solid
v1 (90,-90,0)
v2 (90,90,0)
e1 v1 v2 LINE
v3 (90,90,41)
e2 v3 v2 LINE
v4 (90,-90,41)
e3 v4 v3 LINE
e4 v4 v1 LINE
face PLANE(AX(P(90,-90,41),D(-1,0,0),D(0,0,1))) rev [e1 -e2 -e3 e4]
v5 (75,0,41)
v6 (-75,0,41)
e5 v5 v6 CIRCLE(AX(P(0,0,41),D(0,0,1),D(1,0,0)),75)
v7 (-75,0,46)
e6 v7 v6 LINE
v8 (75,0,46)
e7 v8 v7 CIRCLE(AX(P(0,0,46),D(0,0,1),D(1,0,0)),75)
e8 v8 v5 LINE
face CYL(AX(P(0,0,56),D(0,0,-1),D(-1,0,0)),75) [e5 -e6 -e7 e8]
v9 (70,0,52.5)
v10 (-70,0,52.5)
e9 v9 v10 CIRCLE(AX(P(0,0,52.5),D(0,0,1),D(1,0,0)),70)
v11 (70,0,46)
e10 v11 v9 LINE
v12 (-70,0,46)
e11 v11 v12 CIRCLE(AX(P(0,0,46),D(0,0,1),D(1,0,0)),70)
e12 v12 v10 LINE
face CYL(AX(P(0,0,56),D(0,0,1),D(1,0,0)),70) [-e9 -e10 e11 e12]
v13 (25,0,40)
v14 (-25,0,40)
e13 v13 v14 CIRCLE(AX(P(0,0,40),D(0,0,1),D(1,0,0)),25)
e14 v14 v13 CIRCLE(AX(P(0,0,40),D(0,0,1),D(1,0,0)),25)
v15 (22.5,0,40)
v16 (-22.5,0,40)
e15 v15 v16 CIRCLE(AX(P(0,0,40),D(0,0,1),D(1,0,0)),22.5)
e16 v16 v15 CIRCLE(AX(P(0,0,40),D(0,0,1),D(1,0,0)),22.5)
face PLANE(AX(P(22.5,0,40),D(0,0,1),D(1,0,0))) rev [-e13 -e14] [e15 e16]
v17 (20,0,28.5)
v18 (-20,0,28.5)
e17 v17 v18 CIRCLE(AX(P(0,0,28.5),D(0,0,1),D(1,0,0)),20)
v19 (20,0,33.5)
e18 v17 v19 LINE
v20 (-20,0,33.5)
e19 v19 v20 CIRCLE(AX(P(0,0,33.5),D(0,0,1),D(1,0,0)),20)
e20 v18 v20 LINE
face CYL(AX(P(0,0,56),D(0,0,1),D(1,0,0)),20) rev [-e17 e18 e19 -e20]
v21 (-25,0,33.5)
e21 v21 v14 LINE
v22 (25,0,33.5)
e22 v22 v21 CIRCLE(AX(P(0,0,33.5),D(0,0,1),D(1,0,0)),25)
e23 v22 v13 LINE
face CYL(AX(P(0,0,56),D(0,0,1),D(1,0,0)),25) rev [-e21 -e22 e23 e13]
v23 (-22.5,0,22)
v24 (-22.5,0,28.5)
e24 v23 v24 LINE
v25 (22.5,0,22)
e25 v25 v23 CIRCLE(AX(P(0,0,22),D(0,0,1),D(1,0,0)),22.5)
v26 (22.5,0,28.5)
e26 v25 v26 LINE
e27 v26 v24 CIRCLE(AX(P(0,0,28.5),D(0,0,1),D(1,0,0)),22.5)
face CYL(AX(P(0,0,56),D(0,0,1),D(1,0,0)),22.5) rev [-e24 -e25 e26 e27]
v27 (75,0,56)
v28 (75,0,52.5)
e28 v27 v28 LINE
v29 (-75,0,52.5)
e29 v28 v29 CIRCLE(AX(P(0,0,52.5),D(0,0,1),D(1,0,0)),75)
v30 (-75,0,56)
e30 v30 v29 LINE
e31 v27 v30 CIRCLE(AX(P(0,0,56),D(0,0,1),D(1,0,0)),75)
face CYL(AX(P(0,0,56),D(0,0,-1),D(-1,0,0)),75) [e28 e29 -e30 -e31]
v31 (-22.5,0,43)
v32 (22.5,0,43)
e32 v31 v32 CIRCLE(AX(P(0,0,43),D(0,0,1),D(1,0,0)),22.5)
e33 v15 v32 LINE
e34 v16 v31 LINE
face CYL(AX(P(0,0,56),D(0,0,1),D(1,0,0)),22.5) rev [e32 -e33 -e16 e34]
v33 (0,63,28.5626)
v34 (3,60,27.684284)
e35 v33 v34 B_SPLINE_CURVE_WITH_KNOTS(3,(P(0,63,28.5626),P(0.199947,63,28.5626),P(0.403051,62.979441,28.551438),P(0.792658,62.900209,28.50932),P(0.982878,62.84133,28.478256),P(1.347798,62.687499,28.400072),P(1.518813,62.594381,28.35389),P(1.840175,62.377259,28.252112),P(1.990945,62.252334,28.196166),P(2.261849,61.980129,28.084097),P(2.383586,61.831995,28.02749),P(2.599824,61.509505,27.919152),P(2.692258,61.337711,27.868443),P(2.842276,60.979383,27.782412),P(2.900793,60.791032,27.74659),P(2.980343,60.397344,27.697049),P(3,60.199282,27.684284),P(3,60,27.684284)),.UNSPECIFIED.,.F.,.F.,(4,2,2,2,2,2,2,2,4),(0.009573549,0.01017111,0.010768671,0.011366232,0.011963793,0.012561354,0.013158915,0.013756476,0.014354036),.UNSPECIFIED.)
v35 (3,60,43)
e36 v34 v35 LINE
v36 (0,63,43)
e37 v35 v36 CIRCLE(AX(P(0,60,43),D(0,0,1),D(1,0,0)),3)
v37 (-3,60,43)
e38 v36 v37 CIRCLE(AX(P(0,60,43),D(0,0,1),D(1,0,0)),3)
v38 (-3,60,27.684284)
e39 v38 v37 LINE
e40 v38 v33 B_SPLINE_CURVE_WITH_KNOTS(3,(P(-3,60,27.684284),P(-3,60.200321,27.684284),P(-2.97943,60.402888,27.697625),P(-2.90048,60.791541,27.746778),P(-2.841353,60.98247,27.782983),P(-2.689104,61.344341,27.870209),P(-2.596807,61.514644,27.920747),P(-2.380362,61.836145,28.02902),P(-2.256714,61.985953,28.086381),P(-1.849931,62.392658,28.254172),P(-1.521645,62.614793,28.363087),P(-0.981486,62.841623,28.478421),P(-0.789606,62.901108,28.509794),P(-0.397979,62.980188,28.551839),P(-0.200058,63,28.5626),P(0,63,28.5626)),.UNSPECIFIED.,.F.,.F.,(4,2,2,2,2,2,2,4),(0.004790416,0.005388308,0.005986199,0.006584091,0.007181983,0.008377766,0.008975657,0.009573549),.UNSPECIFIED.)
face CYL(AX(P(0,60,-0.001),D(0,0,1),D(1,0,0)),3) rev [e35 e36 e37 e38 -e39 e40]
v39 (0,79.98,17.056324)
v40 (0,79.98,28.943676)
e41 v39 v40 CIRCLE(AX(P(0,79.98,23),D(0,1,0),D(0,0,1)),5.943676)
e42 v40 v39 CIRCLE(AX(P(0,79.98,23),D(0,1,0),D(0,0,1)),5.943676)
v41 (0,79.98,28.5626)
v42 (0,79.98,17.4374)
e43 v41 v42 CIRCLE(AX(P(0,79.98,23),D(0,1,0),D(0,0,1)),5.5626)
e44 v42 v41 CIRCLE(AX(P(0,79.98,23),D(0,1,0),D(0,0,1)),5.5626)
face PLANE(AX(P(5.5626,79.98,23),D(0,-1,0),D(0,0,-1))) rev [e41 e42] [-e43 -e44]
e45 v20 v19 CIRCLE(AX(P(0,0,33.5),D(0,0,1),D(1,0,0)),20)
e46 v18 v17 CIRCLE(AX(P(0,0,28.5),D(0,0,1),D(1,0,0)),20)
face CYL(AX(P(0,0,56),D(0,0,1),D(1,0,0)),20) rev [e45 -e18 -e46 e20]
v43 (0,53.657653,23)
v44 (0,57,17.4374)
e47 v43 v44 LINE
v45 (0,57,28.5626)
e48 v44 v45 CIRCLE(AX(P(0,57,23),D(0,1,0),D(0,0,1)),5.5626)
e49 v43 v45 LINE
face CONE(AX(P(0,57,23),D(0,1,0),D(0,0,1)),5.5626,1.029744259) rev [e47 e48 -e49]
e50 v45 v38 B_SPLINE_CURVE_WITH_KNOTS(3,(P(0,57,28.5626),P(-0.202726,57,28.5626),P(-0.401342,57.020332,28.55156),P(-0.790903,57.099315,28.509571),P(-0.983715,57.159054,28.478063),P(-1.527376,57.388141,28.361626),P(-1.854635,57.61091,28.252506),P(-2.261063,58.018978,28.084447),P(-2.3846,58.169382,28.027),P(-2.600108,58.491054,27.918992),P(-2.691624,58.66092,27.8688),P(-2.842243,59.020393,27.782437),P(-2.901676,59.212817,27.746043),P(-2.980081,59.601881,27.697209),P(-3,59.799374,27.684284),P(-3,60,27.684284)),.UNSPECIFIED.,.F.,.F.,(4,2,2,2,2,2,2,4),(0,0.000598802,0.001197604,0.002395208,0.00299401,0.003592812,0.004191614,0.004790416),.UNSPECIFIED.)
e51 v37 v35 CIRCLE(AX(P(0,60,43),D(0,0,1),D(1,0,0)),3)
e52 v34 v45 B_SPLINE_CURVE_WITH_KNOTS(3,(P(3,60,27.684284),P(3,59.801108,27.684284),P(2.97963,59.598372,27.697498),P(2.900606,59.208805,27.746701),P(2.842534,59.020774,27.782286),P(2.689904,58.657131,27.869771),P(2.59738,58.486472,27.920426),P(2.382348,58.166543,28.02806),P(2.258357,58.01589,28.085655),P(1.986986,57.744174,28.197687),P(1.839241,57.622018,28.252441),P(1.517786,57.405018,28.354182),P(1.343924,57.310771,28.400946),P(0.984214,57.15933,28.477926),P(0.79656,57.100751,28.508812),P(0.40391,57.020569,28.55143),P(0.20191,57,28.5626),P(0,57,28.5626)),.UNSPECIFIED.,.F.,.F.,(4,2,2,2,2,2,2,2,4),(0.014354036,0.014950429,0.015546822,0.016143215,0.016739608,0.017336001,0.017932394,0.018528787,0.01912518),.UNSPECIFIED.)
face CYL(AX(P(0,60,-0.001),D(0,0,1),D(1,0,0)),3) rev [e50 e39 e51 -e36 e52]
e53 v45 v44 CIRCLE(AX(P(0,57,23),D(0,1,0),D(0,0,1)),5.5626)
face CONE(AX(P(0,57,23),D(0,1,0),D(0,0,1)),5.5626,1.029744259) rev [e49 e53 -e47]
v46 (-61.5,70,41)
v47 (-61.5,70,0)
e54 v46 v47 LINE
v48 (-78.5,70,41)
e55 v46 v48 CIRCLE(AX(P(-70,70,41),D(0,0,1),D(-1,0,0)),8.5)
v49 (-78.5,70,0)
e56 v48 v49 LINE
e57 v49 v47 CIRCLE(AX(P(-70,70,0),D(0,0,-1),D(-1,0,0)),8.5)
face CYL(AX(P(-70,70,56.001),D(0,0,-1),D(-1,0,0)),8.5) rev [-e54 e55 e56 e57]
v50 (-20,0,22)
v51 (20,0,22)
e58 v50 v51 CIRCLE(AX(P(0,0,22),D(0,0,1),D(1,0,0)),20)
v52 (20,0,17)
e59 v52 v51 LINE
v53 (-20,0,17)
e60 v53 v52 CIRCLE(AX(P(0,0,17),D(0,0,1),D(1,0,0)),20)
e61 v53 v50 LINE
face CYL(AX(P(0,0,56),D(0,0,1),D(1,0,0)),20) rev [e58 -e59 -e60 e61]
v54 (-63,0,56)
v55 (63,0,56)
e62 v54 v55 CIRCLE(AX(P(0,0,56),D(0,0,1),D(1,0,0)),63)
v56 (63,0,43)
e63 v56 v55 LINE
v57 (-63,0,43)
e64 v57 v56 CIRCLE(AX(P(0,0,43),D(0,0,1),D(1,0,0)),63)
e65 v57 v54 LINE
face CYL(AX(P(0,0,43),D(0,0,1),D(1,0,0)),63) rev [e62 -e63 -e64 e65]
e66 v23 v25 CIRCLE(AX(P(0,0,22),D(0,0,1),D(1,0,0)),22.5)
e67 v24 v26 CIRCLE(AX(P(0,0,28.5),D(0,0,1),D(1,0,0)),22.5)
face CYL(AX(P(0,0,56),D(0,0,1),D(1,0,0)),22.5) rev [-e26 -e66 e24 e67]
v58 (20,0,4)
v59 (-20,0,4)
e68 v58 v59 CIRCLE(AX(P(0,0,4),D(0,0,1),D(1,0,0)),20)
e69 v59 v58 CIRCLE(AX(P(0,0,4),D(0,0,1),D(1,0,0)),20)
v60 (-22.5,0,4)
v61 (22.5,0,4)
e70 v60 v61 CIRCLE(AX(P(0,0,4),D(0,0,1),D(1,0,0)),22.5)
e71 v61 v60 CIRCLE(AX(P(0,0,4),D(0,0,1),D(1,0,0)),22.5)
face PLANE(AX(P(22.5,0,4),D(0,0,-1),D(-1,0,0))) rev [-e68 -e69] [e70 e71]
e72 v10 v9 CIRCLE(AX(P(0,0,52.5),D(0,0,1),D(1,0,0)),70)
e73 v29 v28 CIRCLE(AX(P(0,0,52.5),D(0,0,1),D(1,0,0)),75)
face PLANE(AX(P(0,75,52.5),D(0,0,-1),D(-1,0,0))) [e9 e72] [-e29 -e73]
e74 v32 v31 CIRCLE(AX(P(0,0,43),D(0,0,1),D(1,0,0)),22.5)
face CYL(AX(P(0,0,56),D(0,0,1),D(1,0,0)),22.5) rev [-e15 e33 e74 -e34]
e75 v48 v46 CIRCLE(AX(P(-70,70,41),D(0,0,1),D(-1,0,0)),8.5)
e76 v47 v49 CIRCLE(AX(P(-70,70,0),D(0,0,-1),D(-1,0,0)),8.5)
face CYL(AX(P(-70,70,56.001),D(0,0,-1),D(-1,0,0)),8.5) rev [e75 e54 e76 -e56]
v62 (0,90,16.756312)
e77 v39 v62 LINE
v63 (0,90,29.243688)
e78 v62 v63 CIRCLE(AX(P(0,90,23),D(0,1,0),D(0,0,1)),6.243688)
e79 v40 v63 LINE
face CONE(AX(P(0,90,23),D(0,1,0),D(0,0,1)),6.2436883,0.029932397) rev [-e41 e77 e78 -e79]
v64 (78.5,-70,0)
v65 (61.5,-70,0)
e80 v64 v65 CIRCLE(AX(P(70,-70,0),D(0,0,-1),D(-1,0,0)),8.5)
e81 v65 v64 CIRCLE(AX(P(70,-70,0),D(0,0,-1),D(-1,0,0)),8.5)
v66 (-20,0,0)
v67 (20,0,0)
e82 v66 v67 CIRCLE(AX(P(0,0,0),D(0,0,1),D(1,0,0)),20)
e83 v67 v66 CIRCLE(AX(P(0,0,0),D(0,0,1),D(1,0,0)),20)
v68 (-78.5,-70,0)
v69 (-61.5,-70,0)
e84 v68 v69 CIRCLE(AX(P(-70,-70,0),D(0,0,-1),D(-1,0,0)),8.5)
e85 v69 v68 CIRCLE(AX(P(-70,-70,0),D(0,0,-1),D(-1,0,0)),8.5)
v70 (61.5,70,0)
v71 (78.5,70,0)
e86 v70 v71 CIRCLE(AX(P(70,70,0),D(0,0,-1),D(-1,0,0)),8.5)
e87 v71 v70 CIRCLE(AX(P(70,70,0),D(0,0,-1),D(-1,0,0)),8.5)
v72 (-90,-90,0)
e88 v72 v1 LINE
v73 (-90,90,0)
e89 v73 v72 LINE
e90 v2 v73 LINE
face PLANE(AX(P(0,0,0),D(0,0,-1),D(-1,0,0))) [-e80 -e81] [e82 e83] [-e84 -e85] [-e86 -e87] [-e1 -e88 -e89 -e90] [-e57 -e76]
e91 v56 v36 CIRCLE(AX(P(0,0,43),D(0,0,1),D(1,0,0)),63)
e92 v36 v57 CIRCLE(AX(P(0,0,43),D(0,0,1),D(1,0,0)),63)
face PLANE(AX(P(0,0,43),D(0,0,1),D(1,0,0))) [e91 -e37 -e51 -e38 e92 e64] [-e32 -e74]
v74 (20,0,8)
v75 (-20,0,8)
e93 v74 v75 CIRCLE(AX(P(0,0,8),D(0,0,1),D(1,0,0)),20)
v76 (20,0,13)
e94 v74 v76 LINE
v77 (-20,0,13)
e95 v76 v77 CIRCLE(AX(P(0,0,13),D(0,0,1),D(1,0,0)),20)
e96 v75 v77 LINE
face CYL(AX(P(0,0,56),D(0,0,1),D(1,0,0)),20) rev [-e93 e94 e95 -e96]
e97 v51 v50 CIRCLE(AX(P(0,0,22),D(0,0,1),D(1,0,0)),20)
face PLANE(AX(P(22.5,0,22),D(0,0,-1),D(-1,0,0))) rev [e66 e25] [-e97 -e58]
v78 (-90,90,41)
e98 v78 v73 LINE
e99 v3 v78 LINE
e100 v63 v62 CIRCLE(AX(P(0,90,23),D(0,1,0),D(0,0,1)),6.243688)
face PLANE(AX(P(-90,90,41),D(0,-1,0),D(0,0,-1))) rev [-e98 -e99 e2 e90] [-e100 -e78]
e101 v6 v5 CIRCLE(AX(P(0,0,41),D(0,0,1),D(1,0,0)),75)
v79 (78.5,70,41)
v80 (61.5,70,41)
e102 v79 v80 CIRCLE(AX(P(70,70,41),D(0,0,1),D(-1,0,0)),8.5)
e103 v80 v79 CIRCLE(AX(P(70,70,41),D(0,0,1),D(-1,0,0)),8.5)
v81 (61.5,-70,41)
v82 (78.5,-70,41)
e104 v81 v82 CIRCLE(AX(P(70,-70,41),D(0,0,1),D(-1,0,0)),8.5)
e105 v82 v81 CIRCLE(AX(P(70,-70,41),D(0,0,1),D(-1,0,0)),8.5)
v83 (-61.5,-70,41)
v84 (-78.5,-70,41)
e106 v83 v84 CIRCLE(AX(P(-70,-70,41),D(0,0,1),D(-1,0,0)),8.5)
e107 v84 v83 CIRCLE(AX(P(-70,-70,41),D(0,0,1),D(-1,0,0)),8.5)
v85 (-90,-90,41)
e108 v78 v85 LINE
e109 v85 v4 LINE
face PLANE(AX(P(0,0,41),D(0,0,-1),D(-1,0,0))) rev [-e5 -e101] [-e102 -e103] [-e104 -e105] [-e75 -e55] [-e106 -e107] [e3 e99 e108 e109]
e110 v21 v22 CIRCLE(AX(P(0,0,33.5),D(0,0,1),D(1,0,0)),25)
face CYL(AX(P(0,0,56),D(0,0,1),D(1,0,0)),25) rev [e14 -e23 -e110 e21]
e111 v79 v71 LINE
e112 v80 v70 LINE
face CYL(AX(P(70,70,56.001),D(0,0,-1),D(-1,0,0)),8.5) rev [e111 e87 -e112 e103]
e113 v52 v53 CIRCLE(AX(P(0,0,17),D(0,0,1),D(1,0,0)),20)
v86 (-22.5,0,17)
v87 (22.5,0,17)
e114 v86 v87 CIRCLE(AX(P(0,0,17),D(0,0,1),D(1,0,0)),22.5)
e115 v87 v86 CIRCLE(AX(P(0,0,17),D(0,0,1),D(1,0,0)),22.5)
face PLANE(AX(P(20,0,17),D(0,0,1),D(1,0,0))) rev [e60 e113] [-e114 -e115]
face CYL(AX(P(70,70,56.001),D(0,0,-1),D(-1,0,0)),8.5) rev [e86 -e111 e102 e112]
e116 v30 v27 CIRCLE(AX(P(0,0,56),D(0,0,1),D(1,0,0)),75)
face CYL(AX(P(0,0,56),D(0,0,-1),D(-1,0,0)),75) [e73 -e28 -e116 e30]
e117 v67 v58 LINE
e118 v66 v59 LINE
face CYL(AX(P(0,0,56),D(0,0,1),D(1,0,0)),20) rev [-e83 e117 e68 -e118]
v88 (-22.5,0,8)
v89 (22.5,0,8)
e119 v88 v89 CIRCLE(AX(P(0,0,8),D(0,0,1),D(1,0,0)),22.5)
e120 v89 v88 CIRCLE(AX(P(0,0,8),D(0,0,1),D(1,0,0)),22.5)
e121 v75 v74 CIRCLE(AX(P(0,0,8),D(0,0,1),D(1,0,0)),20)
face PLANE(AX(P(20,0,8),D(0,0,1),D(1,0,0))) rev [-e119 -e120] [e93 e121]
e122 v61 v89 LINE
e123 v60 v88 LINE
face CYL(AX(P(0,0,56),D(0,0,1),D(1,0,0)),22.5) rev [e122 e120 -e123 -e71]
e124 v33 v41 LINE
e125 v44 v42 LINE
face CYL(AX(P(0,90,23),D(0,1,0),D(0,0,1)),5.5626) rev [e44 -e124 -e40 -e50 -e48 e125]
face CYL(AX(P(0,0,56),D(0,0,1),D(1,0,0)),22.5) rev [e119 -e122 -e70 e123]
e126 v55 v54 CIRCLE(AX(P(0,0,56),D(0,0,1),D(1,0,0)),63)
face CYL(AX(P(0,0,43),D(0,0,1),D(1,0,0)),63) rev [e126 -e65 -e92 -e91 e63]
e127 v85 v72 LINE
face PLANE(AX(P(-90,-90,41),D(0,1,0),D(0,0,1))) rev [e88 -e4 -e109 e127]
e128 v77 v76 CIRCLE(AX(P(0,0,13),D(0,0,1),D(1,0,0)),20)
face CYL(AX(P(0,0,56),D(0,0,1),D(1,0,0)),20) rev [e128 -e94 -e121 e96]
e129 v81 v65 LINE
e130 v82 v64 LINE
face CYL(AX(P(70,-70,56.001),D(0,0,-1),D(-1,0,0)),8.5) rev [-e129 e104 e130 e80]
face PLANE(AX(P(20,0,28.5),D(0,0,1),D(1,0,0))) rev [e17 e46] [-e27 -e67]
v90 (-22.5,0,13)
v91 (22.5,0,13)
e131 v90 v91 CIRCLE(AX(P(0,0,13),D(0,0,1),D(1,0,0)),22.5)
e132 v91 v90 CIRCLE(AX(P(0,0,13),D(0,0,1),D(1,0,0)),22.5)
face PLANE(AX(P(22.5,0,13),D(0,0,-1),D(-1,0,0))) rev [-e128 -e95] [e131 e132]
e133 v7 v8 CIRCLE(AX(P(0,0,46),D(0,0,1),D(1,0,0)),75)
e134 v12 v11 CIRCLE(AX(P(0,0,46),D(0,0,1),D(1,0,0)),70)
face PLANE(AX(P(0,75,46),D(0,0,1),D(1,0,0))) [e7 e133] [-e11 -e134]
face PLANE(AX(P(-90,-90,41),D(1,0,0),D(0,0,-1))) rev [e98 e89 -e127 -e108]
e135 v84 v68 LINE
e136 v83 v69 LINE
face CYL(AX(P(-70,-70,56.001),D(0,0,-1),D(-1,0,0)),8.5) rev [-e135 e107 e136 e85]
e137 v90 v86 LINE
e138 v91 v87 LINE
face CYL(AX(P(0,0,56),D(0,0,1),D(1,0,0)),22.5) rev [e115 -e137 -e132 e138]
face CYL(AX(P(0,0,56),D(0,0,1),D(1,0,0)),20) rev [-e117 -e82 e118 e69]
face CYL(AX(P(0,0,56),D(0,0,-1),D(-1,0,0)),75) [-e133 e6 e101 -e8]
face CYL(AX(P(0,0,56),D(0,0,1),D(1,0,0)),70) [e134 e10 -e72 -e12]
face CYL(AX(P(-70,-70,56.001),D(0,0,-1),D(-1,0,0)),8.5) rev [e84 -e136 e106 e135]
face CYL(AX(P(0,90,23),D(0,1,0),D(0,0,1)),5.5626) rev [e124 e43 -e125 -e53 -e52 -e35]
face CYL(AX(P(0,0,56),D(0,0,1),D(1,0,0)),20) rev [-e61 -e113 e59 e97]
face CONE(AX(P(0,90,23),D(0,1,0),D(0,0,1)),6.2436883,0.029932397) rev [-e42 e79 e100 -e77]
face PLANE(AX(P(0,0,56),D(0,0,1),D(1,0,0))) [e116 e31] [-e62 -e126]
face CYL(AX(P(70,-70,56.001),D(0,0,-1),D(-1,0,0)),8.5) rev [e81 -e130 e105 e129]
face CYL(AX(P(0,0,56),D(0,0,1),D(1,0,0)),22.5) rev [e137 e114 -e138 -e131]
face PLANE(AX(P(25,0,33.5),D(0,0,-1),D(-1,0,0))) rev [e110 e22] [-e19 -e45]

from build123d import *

# Parameters (mm, degrees)
SKETCH_1_W               = 180
SKETCH_1_H               = 180
EXTRUDE_1_DEPTH          = 41
SKETCH_2_R               = 75
EXTRUDE_2_DEPTH          = 15
SKETCH_3_R               = 63
CUT_EXTRUDE_1_DEPTH      = 13
SKETCH_4_W               = 6.5
SKETCH_4_H               = 5
CUT_EXTRUDE_2_REACH      = 136.347
CUT_EXTRUDE_2_END_RADIUS = 5.5626
SKETCH_9_R               = 3
CUT_EXTRUDE_3_REACH      = 141.054
SKETCH_10_R              = 8.5


with BuildPart() as part:
    # 草图1 → 凸台-拉伸1 (new body)
    with BuildSketch(Plane.XY):
        Rectangle(SKETCH_1_W, SKETCH_1_H)
    extrude(amount=EXTRUDE_1_DEPTH)

    # 草图2 → 凸台-拉伸2 (add)
    with BuildSketch(Plane.XY.offset(41)):
        Circle(SKETCH_2_R)
    extrude(amount=EXTRUDE_2_DEPTH)

    # 草图3 → 切除-拉伸1 (cut)
    with BuildSketch(Plane.XY.offset(56)):
        Circle(SKETCH_3_R)
    extrude(amount=-CUT_EXTRUDE_1_DEPTH, mode=Mode.SUBTRACT)

    # 草图4 → 切除-旋转1 (revolve, cut)
    with BuildSketch(Plane(origin=(0, 0, 0), x_dir=(0, 0, -1), z_dir=(1, 0, 0)), mode=Mode.PRIVATE) as cut_revolve_1_sk:
        with Locations((-49.25, 72.5)):
            Rectangle(SKETCH_4_W, SKETCH_4_H)
    revolve(cut_revolve_1_sk.sketch.rotate(Axis((0, 0, 56), (0, 0, -1)), 90), axis=Axis((0, 0, 56), (0, 0, -1)), mode=Mode.SUBTRACT)

    # 草图6 → 1/4 NPT 螺纹孔1 (revolve, cut)
    with BuildSketch(Plane(origin=(0, 90, 23), x_dir=(0, 0, 1), z_dir=(1, 0, 0))):
        Polygon((0, 0), (0, 36.342347279), (5.5626, 33), (5.5626, 10.02), (5.943676082, 10.02), (6.2436883, 0), align=None)
    revolve(axis=Axis((0, 96.35, 23), (0, -1, 0)), mode=Mode.SUBTRACT)

    # 草图8 → 切除-旋转2 (revolve, cut)
    with BuildSketch(Plane(origin=(0, 0, 0), x_dir=(1, 0, 0), z_dir=(0, 1, 0))):
        Polygon((0, -56), (22.5, -56), (22.5, -40), (25, -40), (25, -33.5), (20, -33.5), (20, -28.5), (22.5, -28.5), (22.5, -22), (20, -22), (20, -17), (22.5, -17), (22.5, -13), (20, -13), (20, -8), (22.5, -8), (22.5, -4), (20, -4), (20, 0), (0, 0), align=None)
    revolve(axis=Axis((0, 0, 56), (0, 0, -1)), mode=Mode.SUBTRACT)

    # 切除-拉伸2: up to this cylinder (the profile starts outside it)
    cut_extrude_2_end = Plane(origin=(0, 60, 23), z_dir=(0, 1, 0)) * Cylinder(CUT_EXTRUDE_2_END_RADIUS, 284.8192, mode=Mode.PRIVATE)
    # 草图9 → 切除-拉伸2 (cut, up to the surface)
    with BuildSketch(Plane.XY.offset(43), mode=Mode.PRIVATE) as cut_extrude_2_sk1:
        with Locations(Location((0, 60, 0), (0, 0, 270))):
            Circle(SKETCH_9_R)
    cut_extrude_2_tool1 = extrude(cut_extrude_2_sk1.sketch, amount=-CUT_EXTRUDE_2_REACH, mode=Mode.PRIVATE) - cut_extrude_2_end
    add(cut_extrude_2_tool1.solids().sort_by_distance((0, 60, 43))[0], mode=Mode.SUBTRACT)

    # 草图10 → 切除-拉伸3 (cut, up to next)
    with BuildSketch(Plane(origin=(0, 0, 0), x_dir=(-1, 0, 0), z_dir=(0, 0, -1)), mode=Mode.PRIVATE) as cut_extrude_3_sk1:
        with Locations((-70, 70)):
            Circle(SKETCH_10_R)
    cut_extrude_3_tool1 = extrude(cut_extrude_3_sk1.sketch, amount=-CUT_EXTRUDE_3_REACH, mode=Mode.PRIVATE) & part.part
    # 草图10 → 切除-拉伸3 (cut, up to next)
    with BuildSketch(Plane(origin=(0, 0, 0), x_dir=(-1, 0, 0), z_dir=(0, 0, -1)), mode=Mode.PRIVATE) as cut_extrude_3_sk2:
        with Locations((70, 70)):
            Circle(SKETCH_10_R)
    cut_extrude_3_tool2 = extrude(cut_extrude_3_sk2.sketch, amount=-CUT_EXTRUDE_3_REACH, mode=Mode.PRIVATE) & part.part
    # 草图10 → 切除-拉伸3 (cut, up to next)
    with BuildSketch(Plane(origin=(0, 0, 0), x_dir=(-1, 0, 0), z_dir=(0, 0, -1)), mode=Mode.PRIVATE) as cut_extrude_3_sk3:
        with Locations((70, -70)):
            Circle(SKETCH_10_R)
    cut_extrude_3_tool3 = extrude(cut_extrude_3_sk3.sketch, amount=-CUT_EXTRUDE_3_REACH, mode=Mode.PRIVATE) & part.part
    # 草图10 → 切除-拉伸3 (cut, up to next)
    with BuildSketch(Plane(origin=(0, 0, 0), x_dir=(-1, 0, 0), z_dir=(0, 0, -1)), mode=Mode.PRIVATE) as cut_extrude_3_sk4:
        with Locations((-70, -70)):
            Circle(SKETCH_10_R)
    cut_extrude_3_tool4 = extrude(cut_extrude_3_sk4.sketch, amount=-CUT_EXTRUDE_3_REACH, mode=Mode.PRIVATE) & part.part
    add(cut_extrude_3_tool1.solids().sort_by_distance((70, 70, 0))[0], mode=Mode.SUBTRACT)
    add(cut_extrude_3_tool2.solids().sort_by_distance((-70, 70, 0))[0], mode=Mode.SUBTRACT)
    add(cut_extrude_3_tool3.solids().sort_by_distance((-70, -70, 0))[0], mode=Mode.SUBTRACT)
    add(cut_extrude_3_tool4.solids().sort_by_distance((70, -70, 0))[0], mode=Mode.SUBTRACT)


solid = part.part
